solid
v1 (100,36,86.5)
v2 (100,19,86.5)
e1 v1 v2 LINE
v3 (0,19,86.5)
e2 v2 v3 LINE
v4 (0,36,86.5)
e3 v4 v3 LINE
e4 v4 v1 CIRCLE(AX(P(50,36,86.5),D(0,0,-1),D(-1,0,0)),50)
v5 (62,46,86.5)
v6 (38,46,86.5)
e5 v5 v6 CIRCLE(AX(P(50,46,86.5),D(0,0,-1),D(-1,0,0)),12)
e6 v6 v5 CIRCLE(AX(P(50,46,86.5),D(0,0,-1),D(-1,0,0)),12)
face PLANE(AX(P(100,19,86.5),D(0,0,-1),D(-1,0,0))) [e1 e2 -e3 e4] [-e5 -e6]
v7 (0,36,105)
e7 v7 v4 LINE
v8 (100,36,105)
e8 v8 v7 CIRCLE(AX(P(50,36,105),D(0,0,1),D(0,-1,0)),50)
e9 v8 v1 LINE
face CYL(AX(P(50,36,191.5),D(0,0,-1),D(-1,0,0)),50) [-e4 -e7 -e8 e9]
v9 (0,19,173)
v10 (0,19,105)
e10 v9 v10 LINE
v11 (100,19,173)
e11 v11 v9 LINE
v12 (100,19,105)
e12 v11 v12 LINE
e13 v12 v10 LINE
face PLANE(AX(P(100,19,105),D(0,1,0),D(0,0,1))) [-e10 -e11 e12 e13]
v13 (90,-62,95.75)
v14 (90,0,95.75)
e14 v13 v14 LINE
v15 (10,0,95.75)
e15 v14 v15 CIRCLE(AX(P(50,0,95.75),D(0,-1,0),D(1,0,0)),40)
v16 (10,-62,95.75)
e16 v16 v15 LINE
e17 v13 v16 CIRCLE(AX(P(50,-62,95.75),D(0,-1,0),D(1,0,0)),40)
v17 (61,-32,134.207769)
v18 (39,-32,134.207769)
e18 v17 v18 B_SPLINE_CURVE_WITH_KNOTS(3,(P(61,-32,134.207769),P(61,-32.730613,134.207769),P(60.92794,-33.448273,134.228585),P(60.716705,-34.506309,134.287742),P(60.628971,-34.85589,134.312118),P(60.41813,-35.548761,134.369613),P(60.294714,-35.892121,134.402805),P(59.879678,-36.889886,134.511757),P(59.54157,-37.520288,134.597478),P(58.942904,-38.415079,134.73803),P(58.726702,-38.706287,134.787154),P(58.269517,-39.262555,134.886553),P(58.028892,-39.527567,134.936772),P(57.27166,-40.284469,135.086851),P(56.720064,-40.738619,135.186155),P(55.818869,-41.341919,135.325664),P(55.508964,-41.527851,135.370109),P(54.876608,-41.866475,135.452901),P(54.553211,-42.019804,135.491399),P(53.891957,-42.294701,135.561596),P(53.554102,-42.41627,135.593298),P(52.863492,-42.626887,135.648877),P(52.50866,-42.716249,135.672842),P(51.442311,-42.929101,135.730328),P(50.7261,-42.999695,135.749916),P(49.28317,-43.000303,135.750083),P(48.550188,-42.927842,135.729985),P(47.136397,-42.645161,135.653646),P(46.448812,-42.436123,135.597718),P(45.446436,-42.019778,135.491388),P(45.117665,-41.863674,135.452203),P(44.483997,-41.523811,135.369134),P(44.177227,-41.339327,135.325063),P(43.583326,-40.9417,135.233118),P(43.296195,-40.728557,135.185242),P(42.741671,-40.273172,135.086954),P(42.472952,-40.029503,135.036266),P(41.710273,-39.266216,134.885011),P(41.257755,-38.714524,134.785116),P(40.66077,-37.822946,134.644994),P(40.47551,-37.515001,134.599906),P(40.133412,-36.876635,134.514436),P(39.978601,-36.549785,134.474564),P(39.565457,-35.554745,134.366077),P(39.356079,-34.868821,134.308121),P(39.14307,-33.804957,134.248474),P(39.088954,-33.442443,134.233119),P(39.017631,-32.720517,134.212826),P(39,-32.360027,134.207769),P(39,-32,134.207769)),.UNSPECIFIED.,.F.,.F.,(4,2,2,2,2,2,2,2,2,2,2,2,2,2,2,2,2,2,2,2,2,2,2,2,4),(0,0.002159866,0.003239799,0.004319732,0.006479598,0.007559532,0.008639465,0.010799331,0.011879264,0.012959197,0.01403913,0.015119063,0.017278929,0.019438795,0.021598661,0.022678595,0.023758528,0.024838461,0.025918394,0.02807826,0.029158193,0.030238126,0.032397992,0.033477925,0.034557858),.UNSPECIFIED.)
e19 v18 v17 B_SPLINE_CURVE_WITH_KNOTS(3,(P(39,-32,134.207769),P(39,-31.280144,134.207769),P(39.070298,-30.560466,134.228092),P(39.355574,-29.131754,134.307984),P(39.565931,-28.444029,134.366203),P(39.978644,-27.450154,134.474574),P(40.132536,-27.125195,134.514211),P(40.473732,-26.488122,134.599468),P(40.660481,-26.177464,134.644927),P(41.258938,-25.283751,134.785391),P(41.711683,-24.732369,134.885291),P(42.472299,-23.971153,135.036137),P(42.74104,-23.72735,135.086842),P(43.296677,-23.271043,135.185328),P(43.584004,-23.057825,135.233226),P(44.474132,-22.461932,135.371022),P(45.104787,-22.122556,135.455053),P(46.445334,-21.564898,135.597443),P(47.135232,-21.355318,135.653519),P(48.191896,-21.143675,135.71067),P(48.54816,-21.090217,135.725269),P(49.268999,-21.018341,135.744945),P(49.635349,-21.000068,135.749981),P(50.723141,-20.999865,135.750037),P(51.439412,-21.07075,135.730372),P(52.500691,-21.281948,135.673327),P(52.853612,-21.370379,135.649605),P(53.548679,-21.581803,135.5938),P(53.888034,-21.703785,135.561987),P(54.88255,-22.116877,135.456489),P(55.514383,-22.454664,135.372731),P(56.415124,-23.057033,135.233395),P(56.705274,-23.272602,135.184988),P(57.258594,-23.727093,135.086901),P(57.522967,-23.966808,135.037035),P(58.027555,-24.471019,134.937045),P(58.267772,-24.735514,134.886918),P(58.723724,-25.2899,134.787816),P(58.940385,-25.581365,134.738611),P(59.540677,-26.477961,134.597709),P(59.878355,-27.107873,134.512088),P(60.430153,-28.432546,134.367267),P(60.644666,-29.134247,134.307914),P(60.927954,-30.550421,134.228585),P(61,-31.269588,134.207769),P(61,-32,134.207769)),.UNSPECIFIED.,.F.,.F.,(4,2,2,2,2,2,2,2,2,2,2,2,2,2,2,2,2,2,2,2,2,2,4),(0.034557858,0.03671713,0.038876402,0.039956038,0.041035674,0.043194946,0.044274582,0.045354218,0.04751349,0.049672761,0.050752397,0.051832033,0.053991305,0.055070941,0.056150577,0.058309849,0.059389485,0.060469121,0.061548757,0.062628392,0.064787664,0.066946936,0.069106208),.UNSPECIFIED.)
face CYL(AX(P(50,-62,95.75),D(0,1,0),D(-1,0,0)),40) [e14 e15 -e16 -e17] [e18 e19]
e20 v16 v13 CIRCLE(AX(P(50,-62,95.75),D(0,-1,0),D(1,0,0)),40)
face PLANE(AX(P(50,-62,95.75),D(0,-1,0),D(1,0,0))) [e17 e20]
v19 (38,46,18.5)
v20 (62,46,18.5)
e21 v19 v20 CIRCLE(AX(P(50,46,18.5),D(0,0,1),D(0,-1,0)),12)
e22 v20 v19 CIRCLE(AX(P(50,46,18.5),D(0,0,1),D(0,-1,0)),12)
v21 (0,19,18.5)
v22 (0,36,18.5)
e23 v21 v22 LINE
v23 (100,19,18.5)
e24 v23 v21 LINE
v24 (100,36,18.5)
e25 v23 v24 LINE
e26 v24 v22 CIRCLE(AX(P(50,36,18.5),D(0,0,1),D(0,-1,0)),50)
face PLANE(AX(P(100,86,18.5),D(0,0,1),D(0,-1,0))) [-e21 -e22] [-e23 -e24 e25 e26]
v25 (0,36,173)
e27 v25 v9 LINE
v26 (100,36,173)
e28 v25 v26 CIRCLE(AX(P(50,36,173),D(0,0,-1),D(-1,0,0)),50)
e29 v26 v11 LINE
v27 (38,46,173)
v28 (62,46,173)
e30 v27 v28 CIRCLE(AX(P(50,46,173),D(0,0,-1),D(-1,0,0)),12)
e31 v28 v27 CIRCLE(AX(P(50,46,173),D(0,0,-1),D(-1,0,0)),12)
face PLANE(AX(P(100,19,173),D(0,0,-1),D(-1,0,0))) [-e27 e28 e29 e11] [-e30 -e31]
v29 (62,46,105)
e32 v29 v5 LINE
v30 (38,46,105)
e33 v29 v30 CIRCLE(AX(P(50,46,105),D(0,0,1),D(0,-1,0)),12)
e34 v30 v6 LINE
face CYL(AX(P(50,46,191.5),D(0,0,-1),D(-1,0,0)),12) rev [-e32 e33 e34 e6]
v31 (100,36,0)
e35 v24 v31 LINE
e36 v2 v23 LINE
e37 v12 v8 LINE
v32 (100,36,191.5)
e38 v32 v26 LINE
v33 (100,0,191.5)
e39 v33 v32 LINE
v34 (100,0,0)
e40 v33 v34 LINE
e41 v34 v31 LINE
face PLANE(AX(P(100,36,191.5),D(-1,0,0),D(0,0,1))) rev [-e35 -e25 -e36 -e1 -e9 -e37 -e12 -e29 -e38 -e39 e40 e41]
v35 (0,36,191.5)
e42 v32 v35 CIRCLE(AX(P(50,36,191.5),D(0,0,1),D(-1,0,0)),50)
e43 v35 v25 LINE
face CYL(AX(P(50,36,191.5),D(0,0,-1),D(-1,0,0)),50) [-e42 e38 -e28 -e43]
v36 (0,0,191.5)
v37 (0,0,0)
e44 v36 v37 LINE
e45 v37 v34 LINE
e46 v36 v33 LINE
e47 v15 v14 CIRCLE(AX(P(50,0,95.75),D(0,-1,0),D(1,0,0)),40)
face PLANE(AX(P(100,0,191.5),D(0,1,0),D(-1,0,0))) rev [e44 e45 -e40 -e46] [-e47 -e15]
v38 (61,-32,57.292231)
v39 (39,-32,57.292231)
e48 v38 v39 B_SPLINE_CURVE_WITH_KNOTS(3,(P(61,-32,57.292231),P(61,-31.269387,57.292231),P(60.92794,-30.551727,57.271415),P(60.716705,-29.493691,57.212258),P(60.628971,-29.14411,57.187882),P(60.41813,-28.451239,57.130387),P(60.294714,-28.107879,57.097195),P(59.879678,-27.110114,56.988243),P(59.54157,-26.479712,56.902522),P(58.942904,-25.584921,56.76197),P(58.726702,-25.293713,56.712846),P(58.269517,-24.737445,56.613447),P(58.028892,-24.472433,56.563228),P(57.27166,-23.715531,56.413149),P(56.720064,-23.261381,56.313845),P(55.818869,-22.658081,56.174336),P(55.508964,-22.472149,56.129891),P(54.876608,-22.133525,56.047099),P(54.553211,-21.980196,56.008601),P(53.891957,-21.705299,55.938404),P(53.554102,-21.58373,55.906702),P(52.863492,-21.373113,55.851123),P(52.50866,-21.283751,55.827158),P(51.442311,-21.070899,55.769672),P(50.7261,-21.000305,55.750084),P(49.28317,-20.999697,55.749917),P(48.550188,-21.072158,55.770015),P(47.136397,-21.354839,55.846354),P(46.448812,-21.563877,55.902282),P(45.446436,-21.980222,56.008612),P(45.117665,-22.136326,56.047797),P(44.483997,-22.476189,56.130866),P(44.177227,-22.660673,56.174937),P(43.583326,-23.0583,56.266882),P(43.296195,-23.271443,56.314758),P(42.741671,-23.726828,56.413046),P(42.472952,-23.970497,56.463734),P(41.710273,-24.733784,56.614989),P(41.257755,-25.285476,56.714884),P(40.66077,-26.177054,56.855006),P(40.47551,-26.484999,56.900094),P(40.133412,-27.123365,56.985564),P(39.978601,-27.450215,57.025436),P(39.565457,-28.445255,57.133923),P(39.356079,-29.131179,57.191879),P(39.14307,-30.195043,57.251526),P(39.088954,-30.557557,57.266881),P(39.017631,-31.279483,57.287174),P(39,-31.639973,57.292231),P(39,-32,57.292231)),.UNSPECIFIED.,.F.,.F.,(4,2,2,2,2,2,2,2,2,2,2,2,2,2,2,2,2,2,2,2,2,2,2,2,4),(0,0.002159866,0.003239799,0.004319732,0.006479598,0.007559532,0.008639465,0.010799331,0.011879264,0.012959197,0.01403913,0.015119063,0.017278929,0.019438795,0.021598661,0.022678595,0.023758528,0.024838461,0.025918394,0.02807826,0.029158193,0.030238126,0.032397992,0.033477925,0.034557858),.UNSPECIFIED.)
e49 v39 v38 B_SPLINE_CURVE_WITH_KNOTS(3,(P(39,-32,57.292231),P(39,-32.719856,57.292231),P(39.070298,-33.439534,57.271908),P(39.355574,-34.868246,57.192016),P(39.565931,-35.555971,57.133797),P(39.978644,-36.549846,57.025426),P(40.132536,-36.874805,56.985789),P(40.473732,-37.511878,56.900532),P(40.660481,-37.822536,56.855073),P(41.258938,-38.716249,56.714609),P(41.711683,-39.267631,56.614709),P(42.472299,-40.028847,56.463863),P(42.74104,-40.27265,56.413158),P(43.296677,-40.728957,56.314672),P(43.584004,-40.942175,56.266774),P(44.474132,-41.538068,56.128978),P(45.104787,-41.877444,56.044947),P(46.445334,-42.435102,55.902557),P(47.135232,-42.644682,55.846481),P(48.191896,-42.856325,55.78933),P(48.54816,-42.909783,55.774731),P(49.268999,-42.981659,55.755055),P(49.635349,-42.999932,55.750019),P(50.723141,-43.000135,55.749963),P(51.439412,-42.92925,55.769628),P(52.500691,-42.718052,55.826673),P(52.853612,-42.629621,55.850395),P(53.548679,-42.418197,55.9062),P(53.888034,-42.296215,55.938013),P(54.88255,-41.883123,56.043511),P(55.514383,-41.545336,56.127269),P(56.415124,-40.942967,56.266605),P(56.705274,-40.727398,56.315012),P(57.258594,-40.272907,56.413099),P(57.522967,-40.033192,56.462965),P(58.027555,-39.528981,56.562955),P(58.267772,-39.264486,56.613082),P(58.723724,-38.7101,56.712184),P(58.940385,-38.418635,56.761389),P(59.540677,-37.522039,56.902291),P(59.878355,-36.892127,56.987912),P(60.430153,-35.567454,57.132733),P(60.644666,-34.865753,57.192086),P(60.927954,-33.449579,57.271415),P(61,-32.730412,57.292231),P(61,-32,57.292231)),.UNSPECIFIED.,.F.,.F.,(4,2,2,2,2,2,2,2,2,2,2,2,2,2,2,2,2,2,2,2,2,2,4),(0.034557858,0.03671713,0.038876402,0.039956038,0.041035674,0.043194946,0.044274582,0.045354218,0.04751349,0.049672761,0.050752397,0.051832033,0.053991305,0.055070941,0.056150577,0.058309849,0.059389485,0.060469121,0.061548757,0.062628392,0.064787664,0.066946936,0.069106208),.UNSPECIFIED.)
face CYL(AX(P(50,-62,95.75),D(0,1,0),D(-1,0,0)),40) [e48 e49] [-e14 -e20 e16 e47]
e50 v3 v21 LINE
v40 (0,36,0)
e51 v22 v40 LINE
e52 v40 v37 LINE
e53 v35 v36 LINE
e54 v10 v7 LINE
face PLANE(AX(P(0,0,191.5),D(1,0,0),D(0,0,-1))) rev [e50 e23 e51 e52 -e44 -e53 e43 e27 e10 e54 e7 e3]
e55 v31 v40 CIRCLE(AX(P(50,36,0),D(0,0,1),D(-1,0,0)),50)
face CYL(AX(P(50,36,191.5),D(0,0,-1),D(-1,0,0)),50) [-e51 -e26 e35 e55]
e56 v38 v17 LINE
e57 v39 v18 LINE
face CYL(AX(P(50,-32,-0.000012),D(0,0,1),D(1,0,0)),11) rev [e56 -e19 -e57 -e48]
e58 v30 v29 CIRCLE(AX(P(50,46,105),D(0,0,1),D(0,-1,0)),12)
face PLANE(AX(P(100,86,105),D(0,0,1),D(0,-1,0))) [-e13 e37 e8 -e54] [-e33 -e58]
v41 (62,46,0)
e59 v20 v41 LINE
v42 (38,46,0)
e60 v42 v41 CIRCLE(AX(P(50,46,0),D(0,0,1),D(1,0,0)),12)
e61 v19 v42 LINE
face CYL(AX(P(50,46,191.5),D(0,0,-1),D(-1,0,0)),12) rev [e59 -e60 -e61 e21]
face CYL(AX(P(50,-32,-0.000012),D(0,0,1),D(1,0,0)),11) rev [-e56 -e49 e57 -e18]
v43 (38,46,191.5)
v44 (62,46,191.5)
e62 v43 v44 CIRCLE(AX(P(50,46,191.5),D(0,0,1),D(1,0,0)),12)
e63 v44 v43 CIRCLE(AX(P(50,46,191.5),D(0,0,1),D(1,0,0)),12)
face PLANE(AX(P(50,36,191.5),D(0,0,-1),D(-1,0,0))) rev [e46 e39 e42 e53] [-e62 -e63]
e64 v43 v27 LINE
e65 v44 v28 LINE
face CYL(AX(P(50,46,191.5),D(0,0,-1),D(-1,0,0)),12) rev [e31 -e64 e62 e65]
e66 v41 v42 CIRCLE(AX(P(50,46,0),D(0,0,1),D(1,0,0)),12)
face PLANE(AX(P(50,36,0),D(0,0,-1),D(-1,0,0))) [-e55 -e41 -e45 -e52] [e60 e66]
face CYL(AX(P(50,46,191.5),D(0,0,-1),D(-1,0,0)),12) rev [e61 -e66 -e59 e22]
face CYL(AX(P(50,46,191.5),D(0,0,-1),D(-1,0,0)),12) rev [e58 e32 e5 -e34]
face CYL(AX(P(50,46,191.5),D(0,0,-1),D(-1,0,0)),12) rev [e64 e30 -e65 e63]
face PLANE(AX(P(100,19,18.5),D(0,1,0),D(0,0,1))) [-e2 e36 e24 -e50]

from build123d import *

# Parameters (mm, degrees)
SKETCH1_R               = 12
BOSS_EXTRUDE1_DEPTH     = 191.5
SKETCH2_R               = 40
BOSS_EXTRUDE2_DEPTH     = 62
SKETCH3_W               = 68
SKETCH3_H               = 67
CUT_EXTRUDE5_DEPTH      = 233.52580502
CUT_EXTRUDE8_DEPTH      = 233.52580502
CUT_EXTRUDE8_DEPTH_BACK = 233.52580502
SKETCH4_R               = 11


with BuildPart() as part:
    # Sketch1 → Boss-Extrude1 (new body)
    with BuildSketch(Plane.XY):
        with BuildLine():
            Line((0, 0), (0, 36))
            ThreePointArc((0, 36), (50, 86), (100, 36))
            Line((100, 36), (100, 0))
            Line((100, 0), (0, 0))
        make_face()
        with Locations((50, 46)):
            Circle(SKETCH1_R, mode=Mode.SUBTRACT)
    extrude(amount=BOSS_EXTRUDE1_DEPTH)

    # Sketch2 → Boss-Extrude2 (add)
    with BuildSketch(Plane(origin=(0, 0, 0), x_dir=(-1, 0, 0), z_dir=(0, -1, 0))):
        with Locations(Location((-50, -95.75, 0), (0, 0, 180))):
            Circle(SKETCH2_R)
    extrude(amount=BOSS_EXTRUDE2_DEPTH)

    # Sketch3 → Cut-Extrude5 (cut, through all)
    with BuildSketch(Plane(origin=(0, 0, 0), x_dir=(0, 0, -1), z_dir=(1, 0, 0))):
        with Locations((-52.5, 52.5)):
            Rectangle(SKETCH3_W, SKETCH3_H)
        with Locations((-139, 52.5)):
            Rectangle(SKETCH3_W, SKETCH3_H)
    extrude(amount=CUT_EXTRUDE5_DEPTH, mode=Mode.SUBTRACT)

    # Sketch4 → Cut-Extrude8 (cut, two sides: drawn at the far end of the back side and taken through both)
    with BuildSketch(Plane.XY.offset(-CUT_EXTRUDE8_DEPTH_BACK)):
        with Locations((50, -32)):
            Circle(SKETCH4_R)
    extrude(amount=CUT_EXTRUDE8_DEPTH + CUT_EXTRUDE8_DEPTH_BACK, mode=Mode.SUBTRACT)


solid = part.part
